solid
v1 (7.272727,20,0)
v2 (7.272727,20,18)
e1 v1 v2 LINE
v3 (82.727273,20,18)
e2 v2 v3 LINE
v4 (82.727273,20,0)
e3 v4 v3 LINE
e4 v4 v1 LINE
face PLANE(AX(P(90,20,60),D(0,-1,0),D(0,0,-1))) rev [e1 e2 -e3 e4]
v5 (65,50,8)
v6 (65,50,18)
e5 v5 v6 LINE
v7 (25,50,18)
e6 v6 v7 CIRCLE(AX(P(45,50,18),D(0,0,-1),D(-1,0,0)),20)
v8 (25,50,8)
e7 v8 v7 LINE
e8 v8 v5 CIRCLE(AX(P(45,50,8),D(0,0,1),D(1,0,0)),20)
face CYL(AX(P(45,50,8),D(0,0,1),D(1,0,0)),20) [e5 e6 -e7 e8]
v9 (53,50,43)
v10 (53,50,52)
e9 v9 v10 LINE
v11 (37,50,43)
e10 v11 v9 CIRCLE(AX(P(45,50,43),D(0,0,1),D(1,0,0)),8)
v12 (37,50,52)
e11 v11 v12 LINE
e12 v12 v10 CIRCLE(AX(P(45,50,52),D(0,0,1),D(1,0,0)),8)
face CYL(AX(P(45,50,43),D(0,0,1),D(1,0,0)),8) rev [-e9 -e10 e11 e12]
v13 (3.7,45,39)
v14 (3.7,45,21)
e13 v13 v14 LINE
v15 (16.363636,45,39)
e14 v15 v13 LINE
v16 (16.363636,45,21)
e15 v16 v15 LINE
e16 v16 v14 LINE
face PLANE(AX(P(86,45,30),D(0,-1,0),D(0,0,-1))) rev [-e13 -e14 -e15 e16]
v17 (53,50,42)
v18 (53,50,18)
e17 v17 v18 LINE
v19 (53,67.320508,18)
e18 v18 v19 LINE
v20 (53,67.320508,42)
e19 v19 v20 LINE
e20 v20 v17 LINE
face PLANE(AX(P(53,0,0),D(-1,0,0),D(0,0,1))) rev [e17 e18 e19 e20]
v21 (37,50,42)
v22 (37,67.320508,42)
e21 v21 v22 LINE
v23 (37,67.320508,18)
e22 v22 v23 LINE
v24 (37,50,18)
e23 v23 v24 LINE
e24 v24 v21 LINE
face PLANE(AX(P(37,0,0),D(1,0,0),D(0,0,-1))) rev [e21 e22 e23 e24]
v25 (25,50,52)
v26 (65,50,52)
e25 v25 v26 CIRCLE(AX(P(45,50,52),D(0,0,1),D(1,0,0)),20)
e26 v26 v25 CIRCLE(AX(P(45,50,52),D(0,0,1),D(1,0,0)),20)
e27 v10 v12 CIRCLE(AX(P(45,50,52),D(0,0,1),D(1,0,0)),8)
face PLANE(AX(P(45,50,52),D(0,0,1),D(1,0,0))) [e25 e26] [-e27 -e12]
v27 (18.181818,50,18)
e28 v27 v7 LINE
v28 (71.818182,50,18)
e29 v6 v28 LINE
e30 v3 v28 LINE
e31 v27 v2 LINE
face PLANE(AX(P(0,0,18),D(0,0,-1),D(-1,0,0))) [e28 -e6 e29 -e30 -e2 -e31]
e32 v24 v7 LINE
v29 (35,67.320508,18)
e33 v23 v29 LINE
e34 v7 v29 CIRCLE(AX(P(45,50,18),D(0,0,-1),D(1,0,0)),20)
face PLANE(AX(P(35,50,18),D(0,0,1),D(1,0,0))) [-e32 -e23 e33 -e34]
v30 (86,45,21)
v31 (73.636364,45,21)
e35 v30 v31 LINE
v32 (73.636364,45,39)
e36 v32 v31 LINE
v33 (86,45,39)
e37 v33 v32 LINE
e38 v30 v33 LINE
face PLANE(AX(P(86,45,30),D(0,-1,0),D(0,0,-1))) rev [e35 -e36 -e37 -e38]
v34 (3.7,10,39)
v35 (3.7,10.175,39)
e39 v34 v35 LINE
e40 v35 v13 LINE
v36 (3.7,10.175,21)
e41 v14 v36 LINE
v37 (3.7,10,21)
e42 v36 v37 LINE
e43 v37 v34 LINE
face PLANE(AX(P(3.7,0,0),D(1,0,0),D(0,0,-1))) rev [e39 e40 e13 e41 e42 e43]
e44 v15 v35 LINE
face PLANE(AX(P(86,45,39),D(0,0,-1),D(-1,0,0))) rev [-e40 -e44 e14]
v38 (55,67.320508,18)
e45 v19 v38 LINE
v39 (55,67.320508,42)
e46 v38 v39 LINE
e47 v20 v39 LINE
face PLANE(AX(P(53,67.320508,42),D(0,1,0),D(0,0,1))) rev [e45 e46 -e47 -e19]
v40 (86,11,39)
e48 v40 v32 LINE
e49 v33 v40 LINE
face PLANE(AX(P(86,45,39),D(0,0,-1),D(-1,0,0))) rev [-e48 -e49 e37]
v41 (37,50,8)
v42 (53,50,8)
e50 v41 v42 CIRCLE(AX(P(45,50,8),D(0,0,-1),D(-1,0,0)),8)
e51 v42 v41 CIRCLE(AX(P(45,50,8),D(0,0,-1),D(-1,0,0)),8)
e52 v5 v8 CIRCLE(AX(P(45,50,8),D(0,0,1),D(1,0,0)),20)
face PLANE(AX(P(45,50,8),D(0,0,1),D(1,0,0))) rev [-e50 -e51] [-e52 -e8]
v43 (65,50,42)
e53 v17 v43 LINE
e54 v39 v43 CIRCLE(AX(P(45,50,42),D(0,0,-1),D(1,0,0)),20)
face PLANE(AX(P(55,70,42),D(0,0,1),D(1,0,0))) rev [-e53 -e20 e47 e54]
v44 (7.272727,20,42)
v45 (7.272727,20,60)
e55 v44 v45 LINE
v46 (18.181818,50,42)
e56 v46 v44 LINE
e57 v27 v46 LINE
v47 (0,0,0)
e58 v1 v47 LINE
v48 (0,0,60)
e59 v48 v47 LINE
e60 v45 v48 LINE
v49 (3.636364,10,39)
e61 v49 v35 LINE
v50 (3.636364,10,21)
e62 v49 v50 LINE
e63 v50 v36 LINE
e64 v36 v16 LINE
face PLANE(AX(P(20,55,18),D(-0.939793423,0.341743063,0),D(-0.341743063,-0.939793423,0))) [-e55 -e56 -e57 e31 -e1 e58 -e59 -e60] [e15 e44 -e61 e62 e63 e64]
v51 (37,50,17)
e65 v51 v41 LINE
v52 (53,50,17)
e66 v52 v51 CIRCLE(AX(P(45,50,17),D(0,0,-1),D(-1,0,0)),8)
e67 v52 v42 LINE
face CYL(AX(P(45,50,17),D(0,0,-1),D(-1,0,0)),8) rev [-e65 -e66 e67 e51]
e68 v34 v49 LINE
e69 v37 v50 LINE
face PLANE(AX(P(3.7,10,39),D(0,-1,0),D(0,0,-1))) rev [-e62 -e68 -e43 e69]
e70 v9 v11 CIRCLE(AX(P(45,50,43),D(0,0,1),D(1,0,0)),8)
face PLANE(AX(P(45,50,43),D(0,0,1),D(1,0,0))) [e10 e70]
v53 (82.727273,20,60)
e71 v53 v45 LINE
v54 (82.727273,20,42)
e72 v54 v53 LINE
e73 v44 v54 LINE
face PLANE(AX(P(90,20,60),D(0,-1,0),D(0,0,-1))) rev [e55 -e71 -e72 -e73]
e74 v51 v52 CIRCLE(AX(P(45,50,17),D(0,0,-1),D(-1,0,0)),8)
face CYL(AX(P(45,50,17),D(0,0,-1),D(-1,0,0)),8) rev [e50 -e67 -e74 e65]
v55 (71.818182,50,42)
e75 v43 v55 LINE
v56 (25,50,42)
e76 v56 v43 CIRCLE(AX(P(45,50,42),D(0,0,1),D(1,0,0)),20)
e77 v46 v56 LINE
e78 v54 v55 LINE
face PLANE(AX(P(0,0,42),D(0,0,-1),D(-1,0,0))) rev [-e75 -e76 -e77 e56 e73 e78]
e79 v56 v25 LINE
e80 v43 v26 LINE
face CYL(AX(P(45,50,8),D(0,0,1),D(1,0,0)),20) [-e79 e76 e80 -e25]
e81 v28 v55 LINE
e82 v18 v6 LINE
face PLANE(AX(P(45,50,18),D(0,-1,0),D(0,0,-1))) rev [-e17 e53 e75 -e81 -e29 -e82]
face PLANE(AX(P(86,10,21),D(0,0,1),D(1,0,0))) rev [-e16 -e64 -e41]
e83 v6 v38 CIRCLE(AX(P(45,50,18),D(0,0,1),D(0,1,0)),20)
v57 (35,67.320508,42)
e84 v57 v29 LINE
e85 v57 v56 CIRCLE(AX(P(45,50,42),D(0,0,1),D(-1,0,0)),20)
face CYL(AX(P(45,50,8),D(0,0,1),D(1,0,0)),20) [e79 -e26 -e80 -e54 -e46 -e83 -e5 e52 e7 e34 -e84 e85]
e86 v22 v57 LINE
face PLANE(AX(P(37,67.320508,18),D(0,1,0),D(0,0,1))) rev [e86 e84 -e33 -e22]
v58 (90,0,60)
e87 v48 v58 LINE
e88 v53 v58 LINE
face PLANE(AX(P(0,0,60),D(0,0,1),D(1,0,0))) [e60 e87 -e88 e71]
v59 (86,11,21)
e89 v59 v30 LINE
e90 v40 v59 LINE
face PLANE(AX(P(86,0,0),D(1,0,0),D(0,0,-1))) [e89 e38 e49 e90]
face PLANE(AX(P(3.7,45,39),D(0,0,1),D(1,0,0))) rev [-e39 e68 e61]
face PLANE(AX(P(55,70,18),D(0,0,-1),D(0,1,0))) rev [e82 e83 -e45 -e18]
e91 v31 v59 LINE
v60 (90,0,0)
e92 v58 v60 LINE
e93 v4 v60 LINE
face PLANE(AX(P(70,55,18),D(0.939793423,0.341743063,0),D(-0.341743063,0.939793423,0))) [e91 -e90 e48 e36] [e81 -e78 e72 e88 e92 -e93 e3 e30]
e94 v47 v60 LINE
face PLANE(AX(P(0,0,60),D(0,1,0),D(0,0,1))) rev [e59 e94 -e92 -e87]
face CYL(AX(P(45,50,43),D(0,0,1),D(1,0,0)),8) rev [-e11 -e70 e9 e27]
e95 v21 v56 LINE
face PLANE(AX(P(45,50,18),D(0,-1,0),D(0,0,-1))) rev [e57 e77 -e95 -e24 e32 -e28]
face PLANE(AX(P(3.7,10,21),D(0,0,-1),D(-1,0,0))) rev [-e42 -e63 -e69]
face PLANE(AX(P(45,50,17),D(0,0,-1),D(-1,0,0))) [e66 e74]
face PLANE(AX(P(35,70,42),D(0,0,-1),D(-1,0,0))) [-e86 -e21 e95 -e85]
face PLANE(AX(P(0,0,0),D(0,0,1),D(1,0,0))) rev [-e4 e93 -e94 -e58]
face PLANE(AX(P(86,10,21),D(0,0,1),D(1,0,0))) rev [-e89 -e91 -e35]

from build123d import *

# Parameters (mm, degrees)
BASE_TRAPEZOID_SKETCH_W     = 90
BASE_TRAPEZOID_SKETCH_H     = 20
TRAPEZOID_BASE_DEPTH        = 60
CYLINDER_SUPPORT_DEPTH      = 42
SUPPORT_NOTCH_CUT_DEPTH     = 18
SUPPORT_RELIEF_CUT_DEPTH    = 24
THROUGH_PROFILE_CUT_DEPTH   = 60
CYLINDER_SKETCH_40_R        = 20
CYLINDER_40_DEPTH           = 34
CYLINDER_START              = 10
CYLINDER_EXTENSION_SKETCH_R = 20
CYLINDER_EXTENSION_40_DEPTH = 10
FRONT_BORE_SKETCH_16_R      = 8
FRONT_BORE_16_DEPTH         = 10
REAR_START                  = -10
REAR_BORE_SKETCH_R          = 8
REAR_BORE_DEPTH             = 10
SIDE_BLOCKS_DEPTH           = 86
BLOCK_TRIM_SKETCH_W         = 18
BLOCK_TRIM_SKETCH_H         = 35
BLOCK_TRIM_CUT_DEPTH        = 3.7
SLOT_A_SKETCH_W             = 24
SLOT_A_SKETCH_H             = 20
SLOT_A_CUT_DEPTH            = 10
SLOT_B_SKETCH_W             = 24
SLOT_B_SKETCH_H             = 20
SLOT_B_CUT_DEPTH            = 10
FRONT_START                 = 10
FRONT_BORE_FILL_SKETCH_R    = 8
FRONT_BORE_FILL_DEPTH       = 10
REAR_BORE_FILL_SKETCH_R     = 8
REAR_BORE_FILL_DEPTH        = 10
SLOT_B_FLOOR_SKETCH_W       = 24
SLOT_B_FLOOR_SKETCH_H       = 17.320508076
SLOT_B_FLOOR_CUT_DEPTH      = 2
SLOT_A_FLOOR_SKETCH_W       = 24
SLOT_A_FLOOR_SKETCH_H       = 17.320508076
SLOT_A_FLOOR_CUT_DEPTH      = 2
FRONT_BORE_RECUT_SKETCH_R   = 8
FRONT_BORE_RECUT_DEPTH      = 9
REAR_START_2                = -9
REAR_BORE_RECUT_SKETCH_R    = 8
REAR_BORE_RECUT_DEPTH       = 9


with BuildPart() as part:
    # Base Trapezoid Sketch → Trapezoid Base (new body)
    with BuildSketch(Plane.XY):
        with Locations((45, 10)):
            Rectangle(BASE_TRAPEZOID_SKETCH_W, BASE_TRAPEZOID_SKETCH_H)
    extrude(amount=TRAPEZOID_BASE_DEPTH)

    # Support Profile Sketch → Cylinder Support (add)
    with BuildSketch(Plane.XY.offset(60)):
        Polygon((45, 20), (7.272727273, 20), (20, 55), (45, 55), (70, 55), (82.727272727, 20), align=None)
    extrude(amount=-CYLINDER_SUPPORT_DEPTH)

    # Support Notch Sketch → Support Notch Cut (cut)
    with BuildSketch(Plane.XY.offset(60)):
        Polygon((7.272727273, 20), (20, 55), (70, 55), (82.727272727, 20), align=None)
    extrude(amount=-SUPPORT_NOTCH_CUT_DEPTH, mode=Mode.SUBTRACT)

    # Support Relief Sketch → Support Relief Cut (cut)
    with BuildSketch(Plane.XY.offset(42)):
        Polygon((45, 50), (71.818181818, 50), (70, 55), (20, 55), (18.181818182, 50), align=None)
    extrude(amount=-SUPPORT_RELIEF_CUT_DEPTH, mode=Mode.SUBTRACT)

    # Through Profile Sketch → Through Profile Cut (cut)
    with BuildSketch(Plane.XY.offset(60)):
        Polygon((7.272727273, 20), (0, 20), (0, 0), align=None)
        Polygon((90, 20), (82.727272727, 20), (90, 0), align=None)
    extrude(amount=-THROUGH_PROFILE_CUT_DEPTH, mode=Mode.SUBTRACT)

    # Cylinder Sketch Ø40 → Cylinder Ø40 (add)
    with BuildSketch(Plane.XY.offset(42)):
        with Locations((45, 50)):
            Circle(CYLINDER_SKETCH_40_R)
    extrude(amount=-CYLINDER_40_DEPTH)

    # Cylinder Extension Sketch → Cylinder Extension Ø40 (add)
    with BuildSketch(Plane.XY.offset(42).offset(CYLINDER_START)):
        with Locations((45, 50)):
            Circle(CYLINDER_EXTENSION_SKETCH_R)
    extrude(amount=-CYLINDER_EXTENSION_40_DEPTH)

    # Front Bore Sketch Ø16 → Front Bore Ø16 (cut)
    with BuildSketch(Plane.XY.offset(52)):
        with Locations((45, 50)):
            Circle(FRONT_BORE_SKETCH_16_R)
    extrude(amount=-FRONT_BORE_16_DEPTH, mode=Mode.SUBTRACT)

    # Rear Bore Sketch → Rear Bore (cut)
    with BuildSketch(Plane(origin=(0, 0, 8), x_dir=(-1, 0, 0), z_dir=(0, 0, -1)).offset(REAR_START)):
        with Locations(Location((-45, 50, 0), (0, 0, 180))):
            Circle(REAR_BORE_SKETCH_R)
    extrude(amount=REAR_BORE_DEPTH, mode=Mode.SUBTRACT)

    # Side Block Sketch → Side Blocks (add)
    with BuildSketch(Plane(origin=(0, 0, 0), x_dir=(0, 0, -1), z_dir=(1, 0, 0))):
        Polygon((-30, 45), (-39, 45), (-39, 10), (-21, 10), (-21, 45), align=None)
    extrude(amount=SIDE_BLOCKS_DEPTH)

    # Block Trim Sketch → Block Trim Cut (cut)
    with BuildSketch(Plane.ZY):
        with Locations((30, 27.5)):
            Rectangle(BLOCK_TRIM_SKETCH_W, BLOCK_TRIM_SKETCH_H)
    extrude(amount=-BLOCK_TRIM_CUT_DEPTH, mode=Mode.SUBTRACT)

    # Slot A Sketch → Slot A Cut (cut)
    with BuildSketch(Plane(origin=(65, 0, 0), x_dir=(0, 0, -1), z_dir=(1, 0, 0))):
        with Locations((-30, 60)):
            Rectangle(SLOT_A_SKETCH_W, SLOT_A_SKETCH_H)
    extrude(amount=-SLOT_A_CUT_DEPTH, mode=Mode.SUBTRACT)

    # Slot B Sketch → Slot B Cut (cut)
    with BuildSketch(Plane(origin=(25, 0, 0), x_dir=(0, 0, -1), z_dir=(1, 0, 0))):
        with Locations((-30, 60)):
            Rectangle(SLOT_B_SKETCH_W, SLOT_B_SKETCH_H)
    extrude(amount=SLOT_B_CUT_DEPTH, mode=Mode.SUBTRACT)

    # Front Bore Fill Sketch → Front Bore Fill (add)
    with BuildSketch(Plane.XY.offset(42).offset(FRONT_START)):
        with Locations(Location((45, 50, 0), (0, 0, 180))):
            Circle(FRONT_BORE_FILL_SKETCH_R)
    extrude(amount=-FRONT_BORE_FILL_DEPTH)

    # Rear Bore Fill Sketch → Rear Bore Fill (add)
    with BuildSketch(Plane(origin=(0, 0, 18), x_dir=(-1, 0, 0), z_dir=(0, 0, -1))):
        with Locations((-45, 50)):
            Circle(REAR_BORE_FILL_SKETCH_R)
    extrude(amount=REAR_BORE_FILL_DEPTH)

    # Slot B Floor Sketch → Slot B Floor Cut (cut)
    with BuildSketch(Plane.ZY.offset(-35)):
        with Locations((30, 58.660254038)):
            Rectangle(SLOT_B_FLOOR_SKETCH_W, SLOT_B_FLOOR_SKETCH_H)
    extrude(amount=-SLOT_B_FLOOR_CUT_DEPTH, mode=Mode.SUBTRACT)

    # Slot A Floor Sketch → Slot A Floor Cut (cut)
    with BuildSketch(Plane(origin=(55, 0, 0), x_dir=(0, 0, -1), z_dir=(1, 0, 0))):
        with Locations((-30, 58.660254038)):
            Rectangle(SLOT_A_FLOOR_SKETCH_W, SLOT_A_FLOOR_SKETCH_H)
    extrude(amount=-SLOT_A_FLOOR_CUT_DEPTH, mode=Mode.SUBTRACT)

    # Front Bore Recut Sketch → Front Bore Recut (cut)
    with BuildSketch(Plane.XY.offset(52)):
        with Locations((45, 50)):
            Circle(FRONT_BORE_RECUT_SKETCH_R)
    extrude(amount=-FRONT_BORE_RECUT_DEPTH, mode=Mode.SUBTRACT)

    # Rear Bore Recut Sketch → Rear Bore Recut (cut)
    with BuildSketch(Plane(origin=(0, 0, 8), x_dir=(-1, 0, 0), z_dir=(0, 0, -1)).offset(REAR_START_2)):
        with Locations(Location((-45, 50, 0), (0, 0, 180))):
            Circle(REAR_BORE_RECUT_SKETCH_R)
    extrude(amount=REAR_BORE_RECUT_DEPTH, mode=Mode.SUBTRACT)


solid = part.part
